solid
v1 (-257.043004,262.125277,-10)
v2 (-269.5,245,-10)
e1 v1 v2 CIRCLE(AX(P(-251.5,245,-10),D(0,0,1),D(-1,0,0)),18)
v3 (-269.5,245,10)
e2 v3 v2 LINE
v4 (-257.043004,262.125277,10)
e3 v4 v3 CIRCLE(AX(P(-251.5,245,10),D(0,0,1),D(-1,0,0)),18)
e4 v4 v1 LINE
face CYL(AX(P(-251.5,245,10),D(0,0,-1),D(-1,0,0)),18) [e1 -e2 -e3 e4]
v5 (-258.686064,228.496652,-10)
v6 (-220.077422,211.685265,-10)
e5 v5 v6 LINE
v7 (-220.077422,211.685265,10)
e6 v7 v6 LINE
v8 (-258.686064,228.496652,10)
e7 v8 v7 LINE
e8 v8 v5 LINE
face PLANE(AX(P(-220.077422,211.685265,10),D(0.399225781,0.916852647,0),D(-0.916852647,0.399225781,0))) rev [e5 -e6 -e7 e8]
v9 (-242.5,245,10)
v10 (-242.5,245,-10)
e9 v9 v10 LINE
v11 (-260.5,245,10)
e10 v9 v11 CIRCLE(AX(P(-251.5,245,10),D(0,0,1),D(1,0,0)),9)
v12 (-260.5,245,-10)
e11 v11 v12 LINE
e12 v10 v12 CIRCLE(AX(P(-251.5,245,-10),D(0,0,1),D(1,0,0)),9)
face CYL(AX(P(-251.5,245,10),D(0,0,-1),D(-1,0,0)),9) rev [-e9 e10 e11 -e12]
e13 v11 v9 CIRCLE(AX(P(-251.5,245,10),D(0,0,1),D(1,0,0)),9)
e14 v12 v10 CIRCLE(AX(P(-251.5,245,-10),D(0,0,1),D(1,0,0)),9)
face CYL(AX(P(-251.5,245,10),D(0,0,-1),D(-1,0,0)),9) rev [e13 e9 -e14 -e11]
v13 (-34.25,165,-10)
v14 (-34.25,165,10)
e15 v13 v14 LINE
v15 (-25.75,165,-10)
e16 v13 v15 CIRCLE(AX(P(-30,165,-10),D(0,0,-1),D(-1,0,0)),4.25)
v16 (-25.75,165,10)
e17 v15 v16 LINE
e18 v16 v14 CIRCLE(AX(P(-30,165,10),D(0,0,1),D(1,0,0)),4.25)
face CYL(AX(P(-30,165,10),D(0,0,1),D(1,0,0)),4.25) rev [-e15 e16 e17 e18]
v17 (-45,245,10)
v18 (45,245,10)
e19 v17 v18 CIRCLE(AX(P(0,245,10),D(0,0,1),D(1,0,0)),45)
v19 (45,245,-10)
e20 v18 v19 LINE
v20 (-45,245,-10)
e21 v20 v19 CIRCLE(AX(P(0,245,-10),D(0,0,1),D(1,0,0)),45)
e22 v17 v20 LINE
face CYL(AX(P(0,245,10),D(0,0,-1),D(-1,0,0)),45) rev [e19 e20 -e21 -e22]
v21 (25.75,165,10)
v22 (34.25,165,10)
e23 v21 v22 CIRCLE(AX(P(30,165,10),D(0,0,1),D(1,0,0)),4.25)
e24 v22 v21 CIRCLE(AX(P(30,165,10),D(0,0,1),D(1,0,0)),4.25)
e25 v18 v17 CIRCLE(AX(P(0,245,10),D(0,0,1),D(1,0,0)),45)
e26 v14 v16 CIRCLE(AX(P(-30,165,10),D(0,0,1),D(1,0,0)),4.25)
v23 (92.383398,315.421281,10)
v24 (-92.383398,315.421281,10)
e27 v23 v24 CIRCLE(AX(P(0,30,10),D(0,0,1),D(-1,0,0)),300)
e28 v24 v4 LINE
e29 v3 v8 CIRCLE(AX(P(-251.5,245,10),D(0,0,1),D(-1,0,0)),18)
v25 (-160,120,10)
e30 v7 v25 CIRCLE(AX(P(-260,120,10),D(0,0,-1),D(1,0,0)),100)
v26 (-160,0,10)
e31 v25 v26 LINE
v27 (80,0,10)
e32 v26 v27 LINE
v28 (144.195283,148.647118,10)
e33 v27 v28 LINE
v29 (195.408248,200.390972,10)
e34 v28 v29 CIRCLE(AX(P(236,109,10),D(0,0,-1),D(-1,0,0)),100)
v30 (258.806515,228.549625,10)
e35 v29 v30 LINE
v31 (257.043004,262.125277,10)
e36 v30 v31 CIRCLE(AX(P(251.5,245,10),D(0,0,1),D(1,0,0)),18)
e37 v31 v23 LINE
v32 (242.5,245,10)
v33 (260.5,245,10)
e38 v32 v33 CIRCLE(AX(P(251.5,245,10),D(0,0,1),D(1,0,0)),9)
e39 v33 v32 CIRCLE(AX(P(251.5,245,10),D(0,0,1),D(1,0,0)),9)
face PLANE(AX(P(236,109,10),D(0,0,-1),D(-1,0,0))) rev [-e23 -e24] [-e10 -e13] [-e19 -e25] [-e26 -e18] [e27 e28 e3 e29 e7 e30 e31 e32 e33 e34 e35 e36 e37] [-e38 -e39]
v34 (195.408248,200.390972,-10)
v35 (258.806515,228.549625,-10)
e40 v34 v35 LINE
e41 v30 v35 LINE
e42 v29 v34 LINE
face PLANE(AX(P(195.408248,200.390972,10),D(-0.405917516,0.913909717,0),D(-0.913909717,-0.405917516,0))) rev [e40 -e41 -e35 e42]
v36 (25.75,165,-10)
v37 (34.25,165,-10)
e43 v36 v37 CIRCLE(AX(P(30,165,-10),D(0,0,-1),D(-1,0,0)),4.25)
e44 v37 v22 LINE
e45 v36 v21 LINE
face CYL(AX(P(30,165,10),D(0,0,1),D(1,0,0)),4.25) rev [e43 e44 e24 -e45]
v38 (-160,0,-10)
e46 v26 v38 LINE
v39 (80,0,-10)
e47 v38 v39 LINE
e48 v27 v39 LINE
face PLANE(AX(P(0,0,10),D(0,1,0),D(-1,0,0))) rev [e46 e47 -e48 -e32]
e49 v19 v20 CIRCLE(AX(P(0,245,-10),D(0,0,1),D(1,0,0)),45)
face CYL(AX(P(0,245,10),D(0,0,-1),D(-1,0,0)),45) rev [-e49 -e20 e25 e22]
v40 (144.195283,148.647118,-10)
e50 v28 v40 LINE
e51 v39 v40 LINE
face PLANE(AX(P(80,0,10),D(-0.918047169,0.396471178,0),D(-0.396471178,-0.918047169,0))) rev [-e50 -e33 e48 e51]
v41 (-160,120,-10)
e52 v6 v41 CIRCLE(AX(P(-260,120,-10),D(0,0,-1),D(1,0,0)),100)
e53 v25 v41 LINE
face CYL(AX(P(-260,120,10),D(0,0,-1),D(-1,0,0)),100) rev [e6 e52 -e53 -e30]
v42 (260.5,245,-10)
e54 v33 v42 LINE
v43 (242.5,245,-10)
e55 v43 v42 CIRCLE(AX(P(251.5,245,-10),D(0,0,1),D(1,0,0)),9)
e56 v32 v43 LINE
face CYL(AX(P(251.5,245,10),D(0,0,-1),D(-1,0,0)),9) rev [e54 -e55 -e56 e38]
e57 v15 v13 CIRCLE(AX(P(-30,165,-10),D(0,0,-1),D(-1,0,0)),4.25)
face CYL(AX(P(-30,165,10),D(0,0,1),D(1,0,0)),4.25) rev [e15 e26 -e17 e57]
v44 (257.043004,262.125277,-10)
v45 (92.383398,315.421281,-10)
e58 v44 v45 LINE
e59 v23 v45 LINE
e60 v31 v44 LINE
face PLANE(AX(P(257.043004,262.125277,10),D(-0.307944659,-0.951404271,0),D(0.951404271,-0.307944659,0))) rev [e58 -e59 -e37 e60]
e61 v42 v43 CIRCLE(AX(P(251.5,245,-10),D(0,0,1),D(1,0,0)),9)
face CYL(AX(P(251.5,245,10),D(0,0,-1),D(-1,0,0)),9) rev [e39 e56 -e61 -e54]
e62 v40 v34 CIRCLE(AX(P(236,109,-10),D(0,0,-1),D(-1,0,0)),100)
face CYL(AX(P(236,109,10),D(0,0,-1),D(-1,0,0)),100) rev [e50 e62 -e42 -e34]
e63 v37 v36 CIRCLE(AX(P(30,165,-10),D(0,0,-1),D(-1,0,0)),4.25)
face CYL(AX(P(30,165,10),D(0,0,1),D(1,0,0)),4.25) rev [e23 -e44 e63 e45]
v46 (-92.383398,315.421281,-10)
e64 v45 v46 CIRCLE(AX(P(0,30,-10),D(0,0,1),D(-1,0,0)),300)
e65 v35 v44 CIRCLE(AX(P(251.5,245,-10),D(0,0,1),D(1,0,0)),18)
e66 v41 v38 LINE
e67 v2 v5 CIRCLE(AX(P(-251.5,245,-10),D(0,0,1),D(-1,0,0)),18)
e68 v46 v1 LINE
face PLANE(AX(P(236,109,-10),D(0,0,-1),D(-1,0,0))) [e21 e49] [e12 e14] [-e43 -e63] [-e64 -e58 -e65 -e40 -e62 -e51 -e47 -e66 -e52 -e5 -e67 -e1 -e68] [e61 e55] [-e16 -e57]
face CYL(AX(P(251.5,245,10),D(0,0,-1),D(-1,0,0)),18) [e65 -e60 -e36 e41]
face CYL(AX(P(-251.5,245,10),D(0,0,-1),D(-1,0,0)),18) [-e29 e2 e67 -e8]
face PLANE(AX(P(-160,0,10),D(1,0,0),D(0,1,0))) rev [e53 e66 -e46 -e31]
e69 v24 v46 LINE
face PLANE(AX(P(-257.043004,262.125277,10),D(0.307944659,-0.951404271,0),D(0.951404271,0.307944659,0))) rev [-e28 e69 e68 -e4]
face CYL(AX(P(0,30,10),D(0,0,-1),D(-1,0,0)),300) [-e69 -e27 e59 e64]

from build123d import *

# Parameters (mm, degrees)
SKETCH1_R           = 45
SKETCH1_R_2         = 9
BOSS_EXTRUDE1_DEPTH = 10
M10_TAPPED_HOLE1_D  = 8.5


with BuildPart() as part:
    # Sketch1 → Boss-Extrude1 (new, symmetric)
    with BuildSketch(Plane.XY):
        with BuildLine():
            Line((0, 0), (-160, 0))
            Line((-160, 0), (-160, 120))
            ThreePointArc((-160, 120), (-176.357134778, 174.807582481), (-220.077421949, 211.685264693))
            Line((-220.077421949, 211.685264693), (-258.686064049, 228.496652355))
            ThreePointArc((-258.686064049, 228.496652355), (-269.478553593, 245.878413735), (-257.04300386, 262.12527688))
            Line((-257.04300386, 262.12527688), (-92.383397673, 315.421281327))
            ThreePointArc((-92.383397673, 315.421281327), (0, 330), (92.383397673, 315.421281327))
            Line((92.383397673, 315.421281327), (257.04300386, 262.12527688))
            ThreePointArc((257.04300386, 262.12527688), (269.475222772, 245.944121974), (258.80651528, 228.549625097))
            Line((258.80651528, 228.549625097), (195.408248443, 200.390971685))
            ThreePointArc((195.408248443, 200.390971685), (164.925652867, 179.34512904), (144.195283074, 148.647117803))
            Line((144.195283074, 148.647117803), (80, 0))
            Line((80, 0), (0, 0))
        make_face()
        with Locations((0, 245)):
            Circle(SKETCH1_R, mode=Mode.SUBTRACT)
        with Locations((-251.5, 245)):
            Circle(SKETCH1_R_2, mode=Mode.SUBTRACT)
        with Locations((251.5, 245)):
            Circle(SKETCH1_R_2, mode=Mode.SUBTRACT)
    extrude(amount=BOSS_EXTRUDE1_DEPTH, both=True)

    # M10 Tapped Hole1 (through all)
    with Locations(Plane.XY.offset(10)):
        with Locations((-30, 165), (30, 165)):
            Hole(M10_TAPPED_HOLE1_D / 2)


solid = part.part
